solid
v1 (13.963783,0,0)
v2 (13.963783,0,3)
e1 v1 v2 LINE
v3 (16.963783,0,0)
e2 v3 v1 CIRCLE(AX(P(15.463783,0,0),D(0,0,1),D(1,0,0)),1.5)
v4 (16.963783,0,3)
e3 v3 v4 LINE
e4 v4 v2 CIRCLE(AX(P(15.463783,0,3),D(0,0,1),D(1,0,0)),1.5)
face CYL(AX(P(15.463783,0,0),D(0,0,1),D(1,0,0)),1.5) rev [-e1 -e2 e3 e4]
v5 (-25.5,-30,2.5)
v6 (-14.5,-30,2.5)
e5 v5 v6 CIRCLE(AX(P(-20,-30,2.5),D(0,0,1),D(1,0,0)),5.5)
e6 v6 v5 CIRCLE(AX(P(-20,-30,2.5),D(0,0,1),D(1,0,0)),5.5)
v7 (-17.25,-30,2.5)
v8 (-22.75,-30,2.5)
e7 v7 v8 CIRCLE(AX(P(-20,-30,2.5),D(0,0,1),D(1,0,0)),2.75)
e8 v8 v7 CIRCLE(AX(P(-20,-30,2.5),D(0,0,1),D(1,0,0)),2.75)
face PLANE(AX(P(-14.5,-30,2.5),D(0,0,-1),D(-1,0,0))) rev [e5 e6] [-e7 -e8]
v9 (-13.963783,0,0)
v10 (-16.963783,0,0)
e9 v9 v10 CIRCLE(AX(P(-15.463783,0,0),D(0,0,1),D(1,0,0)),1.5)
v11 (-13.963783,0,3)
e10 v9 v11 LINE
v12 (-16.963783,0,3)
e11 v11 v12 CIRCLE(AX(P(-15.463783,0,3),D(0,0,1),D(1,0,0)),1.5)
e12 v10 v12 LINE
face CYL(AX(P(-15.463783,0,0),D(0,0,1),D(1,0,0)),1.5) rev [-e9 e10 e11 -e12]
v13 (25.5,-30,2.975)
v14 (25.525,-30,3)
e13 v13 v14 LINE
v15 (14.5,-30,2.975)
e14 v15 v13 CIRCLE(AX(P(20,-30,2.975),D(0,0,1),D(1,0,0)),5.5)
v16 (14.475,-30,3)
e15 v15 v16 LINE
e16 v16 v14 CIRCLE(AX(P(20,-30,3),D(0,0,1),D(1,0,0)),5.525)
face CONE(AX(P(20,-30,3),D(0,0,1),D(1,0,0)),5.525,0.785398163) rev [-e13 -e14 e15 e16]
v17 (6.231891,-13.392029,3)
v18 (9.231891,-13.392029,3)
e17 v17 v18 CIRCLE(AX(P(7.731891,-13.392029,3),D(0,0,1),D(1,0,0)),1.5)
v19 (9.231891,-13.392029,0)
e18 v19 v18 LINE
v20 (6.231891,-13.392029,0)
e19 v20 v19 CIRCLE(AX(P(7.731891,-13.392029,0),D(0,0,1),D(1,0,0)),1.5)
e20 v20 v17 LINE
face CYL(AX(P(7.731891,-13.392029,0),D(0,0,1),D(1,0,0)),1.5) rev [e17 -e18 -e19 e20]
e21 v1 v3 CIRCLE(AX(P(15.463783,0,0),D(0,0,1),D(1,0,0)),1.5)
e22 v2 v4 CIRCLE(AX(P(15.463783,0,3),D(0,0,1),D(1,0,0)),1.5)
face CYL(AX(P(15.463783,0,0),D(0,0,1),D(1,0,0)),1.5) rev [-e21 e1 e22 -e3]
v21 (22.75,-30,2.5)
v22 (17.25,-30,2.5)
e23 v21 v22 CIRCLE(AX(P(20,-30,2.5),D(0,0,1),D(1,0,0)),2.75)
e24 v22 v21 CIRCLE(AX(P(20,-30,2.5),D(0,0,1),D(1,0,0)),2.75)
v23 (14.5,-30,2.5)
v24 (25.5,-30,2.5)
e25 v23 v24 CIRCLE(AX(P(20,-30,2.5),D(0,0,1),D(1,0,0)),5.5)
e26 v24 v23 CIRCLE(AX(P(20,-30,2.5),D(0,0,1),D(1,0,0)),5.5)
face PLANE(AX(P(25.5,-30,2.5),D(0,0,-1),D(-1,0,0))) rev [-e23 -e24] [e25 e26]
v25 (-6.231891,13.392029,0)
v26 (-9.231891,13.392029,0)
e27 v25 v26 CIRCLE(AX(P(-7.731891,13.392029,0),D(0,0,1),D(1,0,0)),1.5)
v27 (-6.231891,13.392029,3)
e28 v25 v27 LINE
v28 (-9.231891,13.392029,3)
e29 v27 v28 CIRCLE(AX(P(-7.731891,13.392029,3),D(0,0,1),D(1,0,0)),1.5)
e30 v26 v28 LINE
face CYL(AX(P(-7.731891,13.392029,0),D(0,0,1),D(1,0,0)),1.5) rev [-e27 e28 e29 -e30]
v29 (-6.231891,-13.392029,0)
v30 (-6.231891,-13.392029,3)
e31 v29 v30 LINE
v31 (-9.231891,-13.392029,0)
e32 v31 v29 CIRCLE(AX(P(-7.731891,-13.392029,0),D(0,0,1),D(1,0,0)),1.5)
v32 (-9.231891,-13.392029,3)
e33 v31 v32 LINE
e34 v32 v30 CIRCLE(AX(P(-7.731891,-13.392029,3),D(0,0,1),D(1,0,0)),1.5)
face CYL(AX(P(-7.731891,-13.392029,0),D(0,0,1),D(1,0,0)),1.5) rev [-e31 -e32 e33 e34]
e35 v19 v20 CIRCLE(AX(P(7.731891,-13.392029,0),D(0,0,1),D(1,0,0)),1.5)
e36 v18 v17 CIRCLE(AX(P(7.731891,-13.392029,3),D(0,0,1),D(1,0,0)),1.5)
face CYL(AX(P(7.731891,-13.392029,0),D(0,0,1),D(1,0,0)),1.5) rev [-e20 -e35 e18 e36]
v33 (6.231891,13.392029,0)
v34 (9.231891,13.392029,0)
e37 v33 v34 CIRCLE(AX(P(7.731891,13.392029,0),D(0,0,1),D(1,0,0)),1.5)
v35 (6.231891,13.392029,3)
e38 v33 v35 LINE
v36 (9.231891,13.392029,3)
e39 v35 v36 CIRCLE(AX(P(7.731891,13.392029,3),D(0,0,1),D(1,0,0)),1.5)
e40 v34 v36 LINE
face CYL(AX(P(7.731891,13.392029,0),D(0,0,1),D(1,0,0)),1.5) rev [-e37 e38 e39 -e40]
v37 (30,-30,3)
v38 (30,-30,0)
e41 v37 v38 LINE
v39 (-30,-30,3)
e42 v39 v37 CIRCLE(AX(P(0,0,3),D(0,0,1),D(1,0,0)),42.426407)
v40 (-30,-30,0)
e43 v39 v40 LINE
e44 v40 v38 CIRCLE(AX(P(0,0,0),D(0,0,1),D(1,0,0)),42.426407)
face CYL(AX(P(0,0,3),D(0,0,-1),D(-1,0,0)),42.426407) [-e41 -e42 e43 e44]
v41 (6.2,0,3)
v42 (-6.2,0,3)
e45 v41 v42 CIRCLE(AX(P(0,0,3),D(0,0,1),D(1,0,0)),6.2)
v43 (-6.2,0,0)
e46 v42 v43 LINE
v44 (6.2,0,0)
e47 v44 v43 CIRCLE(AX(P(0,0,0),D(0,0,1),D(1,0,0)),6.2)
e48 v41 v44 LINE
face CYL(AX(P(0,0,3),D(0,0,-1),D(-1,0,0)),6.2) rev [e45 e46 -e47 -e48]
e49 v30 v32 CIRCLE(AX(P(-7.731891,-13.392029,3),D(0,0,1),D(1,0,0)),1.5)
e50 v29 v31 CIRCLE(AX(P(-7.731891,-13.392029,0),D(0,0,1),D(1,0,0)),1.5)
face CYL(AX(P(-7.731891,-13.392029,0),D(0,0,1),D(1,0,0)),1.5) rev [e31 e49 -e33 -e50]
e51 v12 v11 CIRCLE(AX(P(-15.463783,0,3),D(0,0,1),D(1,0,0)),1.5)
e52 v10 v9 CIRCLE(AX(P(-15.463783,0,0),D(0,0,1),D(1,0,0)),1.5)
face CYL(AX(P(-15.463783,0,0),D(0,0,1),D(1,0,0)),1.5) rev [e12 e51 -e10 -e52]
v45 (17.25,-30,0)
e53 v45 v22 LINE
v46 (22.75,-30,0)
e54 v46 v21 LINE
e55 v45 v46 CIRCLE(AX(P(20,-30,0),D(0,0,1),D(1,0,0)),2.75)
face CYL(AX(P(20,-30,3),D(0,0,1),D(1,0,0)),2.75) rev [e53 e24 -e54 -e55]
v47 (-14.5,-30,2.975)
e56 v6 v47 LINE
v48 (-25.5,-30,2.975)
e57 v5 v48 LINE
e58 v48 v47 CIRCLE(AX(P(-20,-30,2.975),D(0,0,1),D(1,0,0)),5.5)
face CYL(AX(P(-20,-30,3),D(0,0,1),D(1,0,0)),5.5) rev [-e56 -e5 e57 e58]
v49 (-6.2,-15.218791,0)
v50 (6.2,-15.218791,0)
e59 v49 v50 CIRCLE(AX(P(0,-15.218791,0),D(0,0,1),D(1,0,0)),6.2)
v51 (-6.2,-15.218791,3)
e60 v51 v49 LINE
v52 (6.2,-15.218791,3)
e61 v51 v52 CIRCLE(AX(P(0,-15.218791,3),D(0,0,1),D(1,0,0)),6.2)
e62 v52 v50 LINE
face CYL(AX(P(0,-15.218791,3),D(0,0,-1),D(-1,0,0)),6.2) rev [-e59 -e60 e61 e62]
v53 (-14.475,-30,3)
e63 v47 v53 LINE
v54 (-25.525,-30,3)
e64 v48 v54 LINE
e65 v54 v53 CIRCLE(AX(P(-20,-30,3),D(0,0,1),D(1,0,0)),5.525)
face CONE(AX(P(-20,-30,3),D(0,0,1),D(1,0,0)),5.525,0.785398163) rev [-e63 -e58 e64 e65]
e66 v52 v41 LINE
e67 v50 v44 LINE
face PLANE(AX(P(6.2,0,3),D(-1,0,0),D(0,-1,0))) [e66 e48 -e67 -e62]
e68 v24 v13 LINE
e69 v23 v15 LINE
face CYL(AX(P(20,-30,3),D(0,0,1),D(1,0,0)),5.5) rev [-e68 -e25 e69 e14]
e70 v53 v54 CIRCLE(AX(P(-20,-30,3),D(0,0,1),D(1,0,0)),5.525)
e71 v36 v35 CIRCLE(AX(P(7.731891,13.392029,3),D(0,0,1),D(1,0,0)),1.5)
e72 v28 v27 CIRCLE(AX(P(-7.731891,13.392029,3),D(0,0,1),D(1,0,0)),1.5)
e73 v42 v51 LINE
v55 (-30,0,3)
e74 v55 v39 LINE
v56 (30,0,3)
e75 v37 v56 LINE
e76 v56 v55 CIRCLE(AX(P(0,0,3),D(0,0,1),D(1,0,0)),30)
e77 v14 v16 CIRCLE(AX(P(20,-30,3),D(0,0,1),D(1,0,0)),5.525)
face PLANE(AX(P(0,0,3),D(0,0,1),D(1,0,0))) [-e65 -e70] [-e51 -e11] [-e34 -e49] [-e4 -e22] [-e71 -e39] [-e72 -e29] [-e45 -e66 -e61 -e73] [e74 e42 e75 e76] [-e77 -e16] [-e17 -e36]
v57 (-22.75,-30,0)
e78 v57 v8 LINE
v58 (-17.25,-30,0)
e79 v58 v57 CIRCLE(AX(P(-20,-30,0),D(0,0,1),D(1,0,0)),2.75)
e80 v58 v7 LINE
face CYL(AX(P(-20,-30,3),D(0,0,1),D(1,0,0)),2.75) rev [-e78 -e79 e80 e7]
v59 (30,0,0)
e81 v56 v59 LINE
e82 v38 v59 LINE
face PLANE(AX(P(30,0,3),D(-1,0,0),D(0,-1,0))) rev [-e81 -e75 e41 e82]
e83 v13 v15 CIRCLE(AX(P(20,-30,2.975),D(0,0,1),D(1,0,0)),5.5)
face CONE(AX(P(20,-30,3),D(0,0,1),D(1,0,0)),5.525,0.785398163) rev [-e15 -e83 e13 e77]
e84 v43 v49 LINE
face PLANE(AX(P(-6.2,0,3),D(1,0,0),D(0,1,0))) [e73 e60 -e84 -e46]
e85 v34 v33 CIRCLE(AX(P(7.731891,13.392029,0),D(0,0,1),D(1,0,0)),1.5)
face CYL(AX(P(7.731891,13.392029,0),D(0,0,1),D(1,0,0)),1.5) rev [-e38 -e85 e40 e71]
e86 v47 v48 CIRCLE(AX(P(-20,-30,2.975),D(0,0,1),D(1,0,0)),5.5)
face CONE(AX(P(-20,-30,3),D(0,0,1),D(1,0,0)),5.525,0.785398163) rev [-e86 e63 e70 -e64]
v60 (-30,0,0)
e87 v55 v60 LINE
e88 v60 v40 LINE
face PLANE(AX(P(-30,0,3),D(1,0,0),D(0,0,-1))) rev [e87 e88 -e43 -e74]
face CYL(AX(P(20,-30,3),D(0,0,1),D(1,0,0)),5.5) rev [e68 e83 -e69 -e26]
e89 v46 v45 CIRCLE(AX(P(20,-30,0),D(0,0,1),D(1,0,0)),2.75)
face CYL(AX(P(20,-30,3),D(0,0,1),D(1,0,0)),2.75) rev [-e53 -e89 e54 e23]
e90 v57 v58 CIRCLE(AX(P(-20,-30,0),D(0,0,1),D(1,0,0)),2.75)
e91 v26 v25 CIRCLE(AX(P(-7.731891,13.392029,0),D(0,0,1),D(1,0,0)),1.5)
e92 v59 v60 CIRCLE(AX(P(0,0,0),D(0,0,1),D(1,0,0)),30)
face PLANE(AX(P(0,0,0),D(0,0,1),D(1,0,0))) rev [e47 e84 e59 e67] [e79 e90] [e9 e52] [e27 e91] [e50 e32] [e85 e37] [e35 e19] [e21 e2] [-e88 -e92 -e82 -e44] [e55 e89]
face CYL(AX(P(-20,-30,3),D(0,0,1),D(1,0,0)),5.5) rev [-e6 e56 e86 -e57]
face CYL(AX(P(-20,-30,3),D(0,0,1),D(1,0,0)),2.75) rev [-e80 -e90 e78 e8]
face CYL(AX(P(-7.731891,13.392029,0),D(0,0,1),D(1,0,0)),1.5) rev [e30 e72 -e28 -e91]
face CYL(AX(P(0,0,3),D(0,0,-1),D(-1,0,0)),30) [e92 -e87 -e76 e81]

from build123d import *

# Parameters (mm, degrees)
BOSS_EXTRUDE1_DEPTH                          = 3
SKETCH11_R                                   = 1.5
CUT_EXTRUDE1_DEPTH                           = 3
CBORE_FOR_M5_HEXAGON_HEAD_BOLTS_FULL_2_COUNT = 2
CBORE_FOR_M5_HEXAGON_HEAD_BOLTS_FULL_2_PITCH = 40


with BuildPart() as part:
    # Sketch4 → Boss-Extrude1 (new body)
    with BuildSketch(Plane.XY):
        with BuildLine():
            Line((30, 0), (30, -30))
            ThreePointArc((30, -30), (0, -42.426406871), (-30, -30))
            Line((-30, -30), (-30, 0))
            ThreePointArc((-30, 0), (0, 30), (30, 0))
        make_face()
        with BuildLine():
            Line((6.2, 0), (6.2, -15.218791378))
            ThreePointArc((6.2, -15.218791378), (0, -21.418791378), (-6.2, -15.218791378))
            Line((-6.2, -15.218791378), (-6.2, 0))
            ThreePointArc((-6.2, 0), (0, 6.2), (6.2, 0))
        make_face(mode=Mode.SUBTRACT)
    extrude(amount=BOSS_EXTRUDE1_DEPTH)

    # Sketch11 → Cut-Extrude1 (cut)
    with BuildSketch(Plane.XY.offset(3)):
        with Locations((-15.463782922, 0)):
            Circle(SKETCH11_R)
        with Locations((-7.731891461, 13.392028849)):
            Circle(SKETCH11_R)
        with Locations((7.731891461, 13.392028849)):
            Circle(SKETCH11_R)
        with Locations((15.463782922, 0)):
            Circle(SKETCH11_R)
        with Locations((7.731891461, -13.392028849)):
            Circle(SKETCH11_R)
        with Locations((-7.731891461, -13.392028849)):
            Circle(SKETCH11_R)
    extrude(amount=-CUT_EXTRUDE1_DEPTH, mode=Mode.SUBTRACT)

    # Sketch14 → CBORE for M5 Hexagon head bolts-Full thread-grade C1 (revolve, cut)
    with BuildSketch(Plane(origin=(20, -30, 3), x_dir=(0, -1, 0), z_dir=(1, 0, 0))):
        Polygon((0, 0), (0, 3), (2.75, 3), (2.75, 0.5), (5.5, 0.5), (5.5, 0.025), (5.525, 0), align=None)
    cbore_for_m5_hexagon_head_bolts_full_thr = revolve(axis=Axis((20, -30, 9.35), (0, 0, -1)), mode=Mode.SUBTRACT)

    # CBORE for M5 Hexagon head bolts-Full 2: CBORE for M5 Hexagon head bolts-Full thread-grade C1 ×2
    with Locations(*[(-i * CBORE_FOR_M5_HEXAGON_HEAD_BOLTS_FULL_2_PITCH, 0, 0) for i in range(1, CBORE_FOR_M5_HEXAGON_HEAD_BOLTS_FULL_2_COUNT)]):
        add(cbore_for_m5_hexagon_head_bolts_full_thr, mode=Mode.SUBTRACT)


solid = part.part
